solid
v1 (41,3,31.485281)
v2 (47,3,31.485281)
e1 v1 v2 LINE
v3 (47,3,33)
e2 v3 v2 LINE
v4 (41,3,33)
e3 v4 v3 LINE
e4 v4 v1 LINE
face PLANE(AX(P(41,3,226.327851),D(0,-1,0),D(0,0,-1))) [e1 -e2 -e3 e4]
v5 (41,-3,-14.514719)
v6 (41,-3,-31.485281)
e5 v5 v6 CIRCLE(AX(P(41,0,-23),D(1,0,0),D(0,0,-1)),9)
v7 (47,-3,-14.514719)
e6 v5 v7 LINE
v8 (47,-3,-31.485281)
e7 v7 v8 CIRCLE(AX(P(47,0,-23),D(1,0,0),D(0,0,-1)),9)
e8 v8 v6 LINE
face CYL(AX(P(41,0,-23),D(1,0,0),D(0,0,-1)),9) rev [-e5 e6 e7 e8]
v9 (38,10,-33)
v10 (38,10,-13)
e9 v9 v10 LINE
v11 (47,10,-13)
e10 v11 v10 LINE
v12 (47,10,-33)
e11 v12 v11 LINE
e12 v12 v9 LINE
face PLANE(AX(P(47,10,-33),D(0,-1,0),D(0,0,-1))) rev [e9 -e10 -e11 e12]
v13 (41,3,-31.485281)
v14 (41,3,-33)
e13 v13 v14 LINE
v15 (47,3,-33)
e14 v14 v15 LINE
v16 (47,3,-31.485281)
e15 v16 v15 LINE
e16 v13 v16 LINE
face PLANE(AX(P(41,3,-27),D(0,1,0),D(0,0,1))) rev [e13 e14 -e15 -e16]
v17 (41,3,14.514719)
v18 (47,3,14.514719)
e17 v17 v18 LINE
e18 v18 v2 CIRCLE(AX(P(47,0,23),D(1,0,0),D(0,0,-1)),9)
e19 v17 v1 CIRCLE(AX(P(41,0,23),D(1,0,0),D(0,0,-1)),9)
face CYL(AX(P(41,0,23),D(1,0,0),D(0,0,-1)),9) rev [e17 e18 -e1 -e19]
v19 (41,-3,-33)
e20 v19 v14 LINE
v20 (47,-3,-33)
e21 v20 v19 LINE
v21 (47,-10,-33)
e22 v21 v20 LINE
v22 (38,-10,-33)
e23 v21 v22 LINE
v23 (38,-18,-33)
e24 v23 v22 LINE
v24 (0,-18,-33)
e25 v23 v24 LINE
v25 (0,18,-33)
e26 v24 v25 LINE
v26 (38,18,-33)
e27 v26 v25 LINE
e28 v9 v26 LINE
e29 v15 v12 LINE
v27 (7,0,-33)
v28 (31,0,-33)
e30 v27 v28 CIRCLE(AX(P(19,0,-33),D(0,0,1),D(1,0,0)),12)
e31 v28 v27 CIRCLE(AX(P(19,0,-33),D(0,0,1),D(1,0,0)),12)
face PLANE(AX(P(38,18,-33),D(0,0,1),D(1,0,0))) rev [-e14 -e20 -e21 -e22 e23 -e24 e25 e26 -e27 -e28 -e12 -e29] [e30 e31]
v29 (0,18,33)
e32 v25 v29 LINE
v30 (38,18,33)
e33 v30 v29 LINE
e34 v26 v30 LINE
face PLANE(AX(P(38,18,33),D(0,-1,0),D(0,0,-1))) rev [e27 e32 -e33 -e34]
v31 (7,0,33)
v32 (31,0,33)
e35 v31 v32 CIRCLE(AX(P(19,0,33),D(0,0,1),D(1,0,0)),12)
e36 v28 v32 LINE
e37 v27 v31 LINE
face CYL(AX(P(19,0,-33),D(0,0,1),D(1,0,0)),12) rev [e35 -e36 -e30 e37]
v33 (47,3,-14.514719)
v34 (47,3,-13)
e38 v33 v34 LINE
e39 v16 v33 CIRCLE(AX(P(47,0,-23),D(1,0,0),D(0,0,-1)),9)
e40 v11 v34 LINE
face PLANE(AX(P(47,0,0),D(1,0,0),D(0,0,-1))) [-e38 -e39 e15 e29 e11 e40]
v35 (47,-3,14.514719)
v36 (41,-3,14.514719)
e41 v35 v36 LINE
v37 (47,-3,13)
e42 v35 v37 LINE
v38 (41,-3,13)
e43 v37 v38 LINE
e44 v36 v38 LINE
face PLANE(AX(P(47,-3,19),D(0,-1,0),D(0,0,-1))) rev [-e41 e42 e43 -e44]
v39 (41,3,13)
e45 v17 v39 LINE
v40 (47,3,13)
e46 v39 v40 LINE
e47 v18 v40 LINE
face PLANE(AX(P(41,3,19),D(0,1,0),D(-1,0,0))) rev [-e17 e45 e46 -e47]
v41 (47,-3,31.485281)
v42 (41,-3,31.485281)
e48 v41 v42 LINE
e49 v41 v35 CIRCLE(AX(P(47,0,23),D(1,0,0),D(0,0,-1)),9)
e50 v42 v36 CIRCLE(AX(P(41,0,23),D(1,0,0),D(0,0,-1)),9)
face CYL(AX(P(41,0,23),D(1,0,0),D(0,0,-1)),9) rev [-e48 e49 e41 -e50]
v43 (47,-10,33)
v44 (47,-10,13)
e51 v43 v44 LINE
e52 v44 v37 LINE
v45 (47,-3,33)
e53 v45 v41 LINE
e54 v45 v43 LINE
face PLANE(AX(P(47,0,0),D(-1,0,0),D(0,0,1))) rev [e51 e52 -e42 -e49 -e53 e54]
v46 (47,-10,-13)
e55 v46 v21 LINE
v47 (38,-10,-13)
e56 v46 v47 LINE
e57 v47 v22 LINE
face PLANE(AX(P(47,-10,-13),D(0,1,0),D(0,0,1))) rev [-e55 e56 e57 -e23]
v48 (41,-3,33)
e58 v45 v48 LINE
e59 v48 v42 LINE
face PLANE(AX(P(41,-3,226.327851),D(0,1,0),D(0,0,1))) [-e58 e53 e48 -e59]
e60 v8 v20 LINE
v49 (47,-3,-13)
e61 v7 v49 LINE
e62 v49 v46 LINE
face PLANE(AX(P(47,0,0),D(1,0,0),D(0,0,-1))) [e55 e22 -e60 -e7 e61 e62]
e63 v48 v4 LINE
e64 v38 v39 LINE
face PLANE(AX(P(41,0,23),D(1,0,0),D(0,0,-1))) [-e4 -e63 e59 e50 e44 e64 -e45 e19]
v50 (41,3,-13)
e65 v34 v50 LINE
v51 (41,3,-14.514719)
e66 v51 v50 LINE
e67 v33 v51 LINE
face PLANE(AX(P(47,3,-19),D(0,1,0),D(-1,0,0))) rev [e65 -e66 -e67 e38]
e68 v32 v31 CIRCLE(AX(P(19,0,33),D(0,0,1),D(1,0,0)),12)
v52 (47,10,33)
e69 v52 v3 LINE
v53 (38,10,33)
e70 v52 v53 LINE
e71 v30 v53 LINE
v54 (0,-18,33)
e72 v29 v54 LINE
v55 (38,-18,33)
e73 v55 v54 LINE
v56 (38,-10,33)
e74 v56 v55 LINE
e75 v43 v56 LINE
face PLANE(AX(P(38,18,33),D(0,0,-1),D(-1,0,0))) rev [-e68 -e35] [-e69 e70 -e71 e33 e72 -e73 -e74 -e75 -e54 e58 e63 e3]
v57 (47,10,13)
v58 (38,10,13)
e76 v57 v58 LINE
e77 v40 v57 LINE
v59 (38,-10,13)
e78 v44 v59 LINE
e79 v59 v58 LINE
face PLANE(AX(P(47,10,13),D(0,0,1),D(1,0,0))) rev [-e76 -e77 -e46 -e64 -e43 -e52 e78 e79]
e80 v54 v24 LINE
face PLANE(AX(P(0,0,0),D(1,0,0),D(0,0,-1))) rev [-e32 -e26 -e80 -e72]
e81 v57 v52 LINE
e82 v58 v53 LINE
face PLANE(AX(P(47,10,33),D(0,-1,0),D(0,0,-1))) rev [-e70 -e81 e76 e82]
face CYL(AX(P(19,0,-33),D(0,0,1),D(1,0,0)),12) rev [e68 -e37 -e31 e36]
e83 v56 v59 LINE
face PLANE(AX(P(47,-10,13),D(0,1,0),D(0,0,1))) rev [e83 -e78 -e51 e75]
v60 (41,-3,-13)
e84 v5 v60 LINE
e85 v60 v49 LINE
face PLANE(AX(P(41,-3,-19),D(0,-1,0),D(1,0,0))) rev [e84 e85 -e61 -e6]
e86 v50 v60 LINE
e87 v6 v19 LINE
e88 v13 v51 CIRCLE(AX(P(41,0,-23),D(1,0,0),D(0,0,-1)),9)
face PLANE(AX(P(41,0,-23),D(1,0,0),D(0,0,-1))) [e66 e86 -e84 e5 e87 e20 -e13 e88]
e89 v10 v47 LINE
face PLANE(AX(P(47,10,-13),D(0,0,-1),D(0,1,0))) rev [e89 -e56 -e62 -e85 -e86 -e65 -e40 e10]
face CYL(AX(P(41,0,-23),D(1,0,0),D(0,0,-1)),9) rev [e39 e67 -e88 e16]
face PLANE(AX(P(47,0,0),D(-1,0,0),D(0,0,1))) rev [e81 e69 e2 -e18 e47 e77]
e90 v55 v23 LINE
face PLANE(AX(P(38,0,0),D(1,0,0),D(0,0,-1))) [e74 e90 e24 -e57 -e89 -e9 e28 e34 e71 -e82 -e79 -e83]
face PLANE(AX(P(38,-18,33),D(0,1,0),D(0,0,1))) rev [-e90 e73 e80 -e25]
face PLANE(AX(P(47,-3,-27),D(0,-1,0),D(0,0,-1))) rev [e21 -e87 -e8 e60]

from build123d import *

# Parameters (mm, degrees)
MAIN_BLOCK_PROFILE_W      = 66
MAIN_BLOCK_PROFILE_H      = 36
MAIN_BLOCK_66X36X38_DEPTH = 38
CLAMP_BOSSES_PROFILE_W    = 20
CLAMP_BOSSES_PROFILE_H    = 20
CLAMP_BOSSES_DEPTH        = 9
SADDLE_CUT_18_A_PROFILE_R = 9
SADDLE_CUT_18_A_DEPTH     = 6
NOTCH_A_3X3_DEPTH         = 84
NOTCH_A_3X3_DEPTH_BACK    = 6
NOTCH_B_3X3_DEPTH         = 6
SADDLE_CUT_18_B_PROFILE_R = 9
SADDLE_CUT_18_B_DEPTH     = 6
NOTCH_C_3X3_DEPTH         = 6
NOTCH_D_PROFILE_W         = 6
NOTCH_D_PROFILE_H         = 6
NOTCH_D_DEPTH             = 6
END_BORE_24_PROFILE_R     = 12
END_BORE_24_DEPTH         = 84


with BuildPart() as part:
    # Main Block Profile → Main Block 66x36x38 (new body)
    with BuildSketch(Plane(origin=(0, 0, 0), x_dir=(0, 0, -1), z_dir=(1, 0, 0))):
        Rectangle(MAIN_BLOCK_PROFILE_W, MAIN_BLOCK_PROFILE_H)
    extrude(amount=MAIN_BLOCK_66X36X38_DEPTH)

    # Clamp Bosses Profile → Clamp Bosses (add)
    with BuildSketch(Plane(origin=(38, 0, 0), x_dir=(0, 0, -1), z_dir=(1, 0, 0))):
        with Locations((-23, 0)):
            Rectangle(CLAMP_BOSSES_PROFILE_W, CLAMP_BOSSES_PROFILE_H)
        with Locations((23, 0)):
            Rectangle(CLAMP_BOSSES_PROFILE_W, CLAMP_BOSSES_PROFILE_H)
    extrude(amount=CLAMP_BOSSES_DEPTH)

    # Saddle Cut Ø18 A Profile → Saddle Cut Ø18 A (cut)
    with BuildSketch(Plane(origin=(47, 0, 0), x_dir=(0, 0, -1), z_dir=(1, 0, 0))):
        with Locations((-23, 0)):
            Circle(SADDLE_CUT_18_A_PROFILE_R)
    extrude(amount=-SADDLE_CUT_18_A_DEPTH, mode=Mode.SUBTRACT)

    # Notch A Profile → Notch A 3x3 (cut, two sides: drawn at the far end of the back side and taken through both)
    with BuildSketch(Plane.XY.offset(33).offset(-NOTCH_A_3X3_DEPTH_BACK)):
        Polygon((41, 3), (41, 0), (41, -3), (47, -3), (47, 3), align=None)
    extrude(amount=NOTCH_A_3X3_DEPTH + NOTCH_A_3X3_DEPTH_BACK, mode=Mode.SUBTRACT)

    # Notch B Profile → Notch B 3x3 (cut)
    with BuildSketch(Plane(origin=(0, 0, 13), x_dir=(-1, 0, 0), z_dir=(0, 0, -1))):
        Polygon((-41, 0), (-41, 3), (-47, 3), (-47, -3), (-41, -3), align=None)
    extrude(amount=-NOTCH_B_3X3_DEPTH, mode=Mode.SUBTRACT)

    # Saddle Cut Ø18 B Profile → Saddle Cut Ø18 B (cut)
    with BuildSketch(Plane(origin=(47, 0, 0), x_dir=(0, 0, -1), z_dir=(1, 0, 0))):
        with Locations((23, 0)):
            Circle(SADDLE_CUT_18_B_PROFILE_R)
    extrude(amount=-SADDLE_CUT_18_B_DEPTH, mode=Mode.SUBTRACT)

    # Notch C Profile → Notch C 3x3 (cut)
    with BuildSketch(Plane(origin=(0, 0, -33), x_dir=(-1, 0, 0), z_dir=(0, 0, -1))):
        Polygon((-41, 0), (-41, 3), (-47, 3), (-47, -3), (-41, -3), align=None)
    extrude(amount=-NOTCH_C_3X3_DEPTH, mode=Mode.SUBTRACT)

    # Notch D Profile → Notch D (cut)
    with BuildSketch(Plane.XY.offset(-13)):
        with Locations((44, 0)):
            Rectangle(NOTCH_D_PROFILE_W, NOTCH_D_PROFILE_H)
    extrude(amount=-NOTCH_D_DEPTH, mode=Mode.SUBTRACT)

    # End Bore Ø24 Profile → End Bore Ø24 (cut, through all)
    with BuildSketch(Plane.XY.offset(33)):
        with Locations((19, 0)):
            Circle(END_BORE_24_PROFILE_R)
    extrude(amount=-END_BORE_24_DEPTH, mode=Mode.SUBTRACT)


solid = part.part
